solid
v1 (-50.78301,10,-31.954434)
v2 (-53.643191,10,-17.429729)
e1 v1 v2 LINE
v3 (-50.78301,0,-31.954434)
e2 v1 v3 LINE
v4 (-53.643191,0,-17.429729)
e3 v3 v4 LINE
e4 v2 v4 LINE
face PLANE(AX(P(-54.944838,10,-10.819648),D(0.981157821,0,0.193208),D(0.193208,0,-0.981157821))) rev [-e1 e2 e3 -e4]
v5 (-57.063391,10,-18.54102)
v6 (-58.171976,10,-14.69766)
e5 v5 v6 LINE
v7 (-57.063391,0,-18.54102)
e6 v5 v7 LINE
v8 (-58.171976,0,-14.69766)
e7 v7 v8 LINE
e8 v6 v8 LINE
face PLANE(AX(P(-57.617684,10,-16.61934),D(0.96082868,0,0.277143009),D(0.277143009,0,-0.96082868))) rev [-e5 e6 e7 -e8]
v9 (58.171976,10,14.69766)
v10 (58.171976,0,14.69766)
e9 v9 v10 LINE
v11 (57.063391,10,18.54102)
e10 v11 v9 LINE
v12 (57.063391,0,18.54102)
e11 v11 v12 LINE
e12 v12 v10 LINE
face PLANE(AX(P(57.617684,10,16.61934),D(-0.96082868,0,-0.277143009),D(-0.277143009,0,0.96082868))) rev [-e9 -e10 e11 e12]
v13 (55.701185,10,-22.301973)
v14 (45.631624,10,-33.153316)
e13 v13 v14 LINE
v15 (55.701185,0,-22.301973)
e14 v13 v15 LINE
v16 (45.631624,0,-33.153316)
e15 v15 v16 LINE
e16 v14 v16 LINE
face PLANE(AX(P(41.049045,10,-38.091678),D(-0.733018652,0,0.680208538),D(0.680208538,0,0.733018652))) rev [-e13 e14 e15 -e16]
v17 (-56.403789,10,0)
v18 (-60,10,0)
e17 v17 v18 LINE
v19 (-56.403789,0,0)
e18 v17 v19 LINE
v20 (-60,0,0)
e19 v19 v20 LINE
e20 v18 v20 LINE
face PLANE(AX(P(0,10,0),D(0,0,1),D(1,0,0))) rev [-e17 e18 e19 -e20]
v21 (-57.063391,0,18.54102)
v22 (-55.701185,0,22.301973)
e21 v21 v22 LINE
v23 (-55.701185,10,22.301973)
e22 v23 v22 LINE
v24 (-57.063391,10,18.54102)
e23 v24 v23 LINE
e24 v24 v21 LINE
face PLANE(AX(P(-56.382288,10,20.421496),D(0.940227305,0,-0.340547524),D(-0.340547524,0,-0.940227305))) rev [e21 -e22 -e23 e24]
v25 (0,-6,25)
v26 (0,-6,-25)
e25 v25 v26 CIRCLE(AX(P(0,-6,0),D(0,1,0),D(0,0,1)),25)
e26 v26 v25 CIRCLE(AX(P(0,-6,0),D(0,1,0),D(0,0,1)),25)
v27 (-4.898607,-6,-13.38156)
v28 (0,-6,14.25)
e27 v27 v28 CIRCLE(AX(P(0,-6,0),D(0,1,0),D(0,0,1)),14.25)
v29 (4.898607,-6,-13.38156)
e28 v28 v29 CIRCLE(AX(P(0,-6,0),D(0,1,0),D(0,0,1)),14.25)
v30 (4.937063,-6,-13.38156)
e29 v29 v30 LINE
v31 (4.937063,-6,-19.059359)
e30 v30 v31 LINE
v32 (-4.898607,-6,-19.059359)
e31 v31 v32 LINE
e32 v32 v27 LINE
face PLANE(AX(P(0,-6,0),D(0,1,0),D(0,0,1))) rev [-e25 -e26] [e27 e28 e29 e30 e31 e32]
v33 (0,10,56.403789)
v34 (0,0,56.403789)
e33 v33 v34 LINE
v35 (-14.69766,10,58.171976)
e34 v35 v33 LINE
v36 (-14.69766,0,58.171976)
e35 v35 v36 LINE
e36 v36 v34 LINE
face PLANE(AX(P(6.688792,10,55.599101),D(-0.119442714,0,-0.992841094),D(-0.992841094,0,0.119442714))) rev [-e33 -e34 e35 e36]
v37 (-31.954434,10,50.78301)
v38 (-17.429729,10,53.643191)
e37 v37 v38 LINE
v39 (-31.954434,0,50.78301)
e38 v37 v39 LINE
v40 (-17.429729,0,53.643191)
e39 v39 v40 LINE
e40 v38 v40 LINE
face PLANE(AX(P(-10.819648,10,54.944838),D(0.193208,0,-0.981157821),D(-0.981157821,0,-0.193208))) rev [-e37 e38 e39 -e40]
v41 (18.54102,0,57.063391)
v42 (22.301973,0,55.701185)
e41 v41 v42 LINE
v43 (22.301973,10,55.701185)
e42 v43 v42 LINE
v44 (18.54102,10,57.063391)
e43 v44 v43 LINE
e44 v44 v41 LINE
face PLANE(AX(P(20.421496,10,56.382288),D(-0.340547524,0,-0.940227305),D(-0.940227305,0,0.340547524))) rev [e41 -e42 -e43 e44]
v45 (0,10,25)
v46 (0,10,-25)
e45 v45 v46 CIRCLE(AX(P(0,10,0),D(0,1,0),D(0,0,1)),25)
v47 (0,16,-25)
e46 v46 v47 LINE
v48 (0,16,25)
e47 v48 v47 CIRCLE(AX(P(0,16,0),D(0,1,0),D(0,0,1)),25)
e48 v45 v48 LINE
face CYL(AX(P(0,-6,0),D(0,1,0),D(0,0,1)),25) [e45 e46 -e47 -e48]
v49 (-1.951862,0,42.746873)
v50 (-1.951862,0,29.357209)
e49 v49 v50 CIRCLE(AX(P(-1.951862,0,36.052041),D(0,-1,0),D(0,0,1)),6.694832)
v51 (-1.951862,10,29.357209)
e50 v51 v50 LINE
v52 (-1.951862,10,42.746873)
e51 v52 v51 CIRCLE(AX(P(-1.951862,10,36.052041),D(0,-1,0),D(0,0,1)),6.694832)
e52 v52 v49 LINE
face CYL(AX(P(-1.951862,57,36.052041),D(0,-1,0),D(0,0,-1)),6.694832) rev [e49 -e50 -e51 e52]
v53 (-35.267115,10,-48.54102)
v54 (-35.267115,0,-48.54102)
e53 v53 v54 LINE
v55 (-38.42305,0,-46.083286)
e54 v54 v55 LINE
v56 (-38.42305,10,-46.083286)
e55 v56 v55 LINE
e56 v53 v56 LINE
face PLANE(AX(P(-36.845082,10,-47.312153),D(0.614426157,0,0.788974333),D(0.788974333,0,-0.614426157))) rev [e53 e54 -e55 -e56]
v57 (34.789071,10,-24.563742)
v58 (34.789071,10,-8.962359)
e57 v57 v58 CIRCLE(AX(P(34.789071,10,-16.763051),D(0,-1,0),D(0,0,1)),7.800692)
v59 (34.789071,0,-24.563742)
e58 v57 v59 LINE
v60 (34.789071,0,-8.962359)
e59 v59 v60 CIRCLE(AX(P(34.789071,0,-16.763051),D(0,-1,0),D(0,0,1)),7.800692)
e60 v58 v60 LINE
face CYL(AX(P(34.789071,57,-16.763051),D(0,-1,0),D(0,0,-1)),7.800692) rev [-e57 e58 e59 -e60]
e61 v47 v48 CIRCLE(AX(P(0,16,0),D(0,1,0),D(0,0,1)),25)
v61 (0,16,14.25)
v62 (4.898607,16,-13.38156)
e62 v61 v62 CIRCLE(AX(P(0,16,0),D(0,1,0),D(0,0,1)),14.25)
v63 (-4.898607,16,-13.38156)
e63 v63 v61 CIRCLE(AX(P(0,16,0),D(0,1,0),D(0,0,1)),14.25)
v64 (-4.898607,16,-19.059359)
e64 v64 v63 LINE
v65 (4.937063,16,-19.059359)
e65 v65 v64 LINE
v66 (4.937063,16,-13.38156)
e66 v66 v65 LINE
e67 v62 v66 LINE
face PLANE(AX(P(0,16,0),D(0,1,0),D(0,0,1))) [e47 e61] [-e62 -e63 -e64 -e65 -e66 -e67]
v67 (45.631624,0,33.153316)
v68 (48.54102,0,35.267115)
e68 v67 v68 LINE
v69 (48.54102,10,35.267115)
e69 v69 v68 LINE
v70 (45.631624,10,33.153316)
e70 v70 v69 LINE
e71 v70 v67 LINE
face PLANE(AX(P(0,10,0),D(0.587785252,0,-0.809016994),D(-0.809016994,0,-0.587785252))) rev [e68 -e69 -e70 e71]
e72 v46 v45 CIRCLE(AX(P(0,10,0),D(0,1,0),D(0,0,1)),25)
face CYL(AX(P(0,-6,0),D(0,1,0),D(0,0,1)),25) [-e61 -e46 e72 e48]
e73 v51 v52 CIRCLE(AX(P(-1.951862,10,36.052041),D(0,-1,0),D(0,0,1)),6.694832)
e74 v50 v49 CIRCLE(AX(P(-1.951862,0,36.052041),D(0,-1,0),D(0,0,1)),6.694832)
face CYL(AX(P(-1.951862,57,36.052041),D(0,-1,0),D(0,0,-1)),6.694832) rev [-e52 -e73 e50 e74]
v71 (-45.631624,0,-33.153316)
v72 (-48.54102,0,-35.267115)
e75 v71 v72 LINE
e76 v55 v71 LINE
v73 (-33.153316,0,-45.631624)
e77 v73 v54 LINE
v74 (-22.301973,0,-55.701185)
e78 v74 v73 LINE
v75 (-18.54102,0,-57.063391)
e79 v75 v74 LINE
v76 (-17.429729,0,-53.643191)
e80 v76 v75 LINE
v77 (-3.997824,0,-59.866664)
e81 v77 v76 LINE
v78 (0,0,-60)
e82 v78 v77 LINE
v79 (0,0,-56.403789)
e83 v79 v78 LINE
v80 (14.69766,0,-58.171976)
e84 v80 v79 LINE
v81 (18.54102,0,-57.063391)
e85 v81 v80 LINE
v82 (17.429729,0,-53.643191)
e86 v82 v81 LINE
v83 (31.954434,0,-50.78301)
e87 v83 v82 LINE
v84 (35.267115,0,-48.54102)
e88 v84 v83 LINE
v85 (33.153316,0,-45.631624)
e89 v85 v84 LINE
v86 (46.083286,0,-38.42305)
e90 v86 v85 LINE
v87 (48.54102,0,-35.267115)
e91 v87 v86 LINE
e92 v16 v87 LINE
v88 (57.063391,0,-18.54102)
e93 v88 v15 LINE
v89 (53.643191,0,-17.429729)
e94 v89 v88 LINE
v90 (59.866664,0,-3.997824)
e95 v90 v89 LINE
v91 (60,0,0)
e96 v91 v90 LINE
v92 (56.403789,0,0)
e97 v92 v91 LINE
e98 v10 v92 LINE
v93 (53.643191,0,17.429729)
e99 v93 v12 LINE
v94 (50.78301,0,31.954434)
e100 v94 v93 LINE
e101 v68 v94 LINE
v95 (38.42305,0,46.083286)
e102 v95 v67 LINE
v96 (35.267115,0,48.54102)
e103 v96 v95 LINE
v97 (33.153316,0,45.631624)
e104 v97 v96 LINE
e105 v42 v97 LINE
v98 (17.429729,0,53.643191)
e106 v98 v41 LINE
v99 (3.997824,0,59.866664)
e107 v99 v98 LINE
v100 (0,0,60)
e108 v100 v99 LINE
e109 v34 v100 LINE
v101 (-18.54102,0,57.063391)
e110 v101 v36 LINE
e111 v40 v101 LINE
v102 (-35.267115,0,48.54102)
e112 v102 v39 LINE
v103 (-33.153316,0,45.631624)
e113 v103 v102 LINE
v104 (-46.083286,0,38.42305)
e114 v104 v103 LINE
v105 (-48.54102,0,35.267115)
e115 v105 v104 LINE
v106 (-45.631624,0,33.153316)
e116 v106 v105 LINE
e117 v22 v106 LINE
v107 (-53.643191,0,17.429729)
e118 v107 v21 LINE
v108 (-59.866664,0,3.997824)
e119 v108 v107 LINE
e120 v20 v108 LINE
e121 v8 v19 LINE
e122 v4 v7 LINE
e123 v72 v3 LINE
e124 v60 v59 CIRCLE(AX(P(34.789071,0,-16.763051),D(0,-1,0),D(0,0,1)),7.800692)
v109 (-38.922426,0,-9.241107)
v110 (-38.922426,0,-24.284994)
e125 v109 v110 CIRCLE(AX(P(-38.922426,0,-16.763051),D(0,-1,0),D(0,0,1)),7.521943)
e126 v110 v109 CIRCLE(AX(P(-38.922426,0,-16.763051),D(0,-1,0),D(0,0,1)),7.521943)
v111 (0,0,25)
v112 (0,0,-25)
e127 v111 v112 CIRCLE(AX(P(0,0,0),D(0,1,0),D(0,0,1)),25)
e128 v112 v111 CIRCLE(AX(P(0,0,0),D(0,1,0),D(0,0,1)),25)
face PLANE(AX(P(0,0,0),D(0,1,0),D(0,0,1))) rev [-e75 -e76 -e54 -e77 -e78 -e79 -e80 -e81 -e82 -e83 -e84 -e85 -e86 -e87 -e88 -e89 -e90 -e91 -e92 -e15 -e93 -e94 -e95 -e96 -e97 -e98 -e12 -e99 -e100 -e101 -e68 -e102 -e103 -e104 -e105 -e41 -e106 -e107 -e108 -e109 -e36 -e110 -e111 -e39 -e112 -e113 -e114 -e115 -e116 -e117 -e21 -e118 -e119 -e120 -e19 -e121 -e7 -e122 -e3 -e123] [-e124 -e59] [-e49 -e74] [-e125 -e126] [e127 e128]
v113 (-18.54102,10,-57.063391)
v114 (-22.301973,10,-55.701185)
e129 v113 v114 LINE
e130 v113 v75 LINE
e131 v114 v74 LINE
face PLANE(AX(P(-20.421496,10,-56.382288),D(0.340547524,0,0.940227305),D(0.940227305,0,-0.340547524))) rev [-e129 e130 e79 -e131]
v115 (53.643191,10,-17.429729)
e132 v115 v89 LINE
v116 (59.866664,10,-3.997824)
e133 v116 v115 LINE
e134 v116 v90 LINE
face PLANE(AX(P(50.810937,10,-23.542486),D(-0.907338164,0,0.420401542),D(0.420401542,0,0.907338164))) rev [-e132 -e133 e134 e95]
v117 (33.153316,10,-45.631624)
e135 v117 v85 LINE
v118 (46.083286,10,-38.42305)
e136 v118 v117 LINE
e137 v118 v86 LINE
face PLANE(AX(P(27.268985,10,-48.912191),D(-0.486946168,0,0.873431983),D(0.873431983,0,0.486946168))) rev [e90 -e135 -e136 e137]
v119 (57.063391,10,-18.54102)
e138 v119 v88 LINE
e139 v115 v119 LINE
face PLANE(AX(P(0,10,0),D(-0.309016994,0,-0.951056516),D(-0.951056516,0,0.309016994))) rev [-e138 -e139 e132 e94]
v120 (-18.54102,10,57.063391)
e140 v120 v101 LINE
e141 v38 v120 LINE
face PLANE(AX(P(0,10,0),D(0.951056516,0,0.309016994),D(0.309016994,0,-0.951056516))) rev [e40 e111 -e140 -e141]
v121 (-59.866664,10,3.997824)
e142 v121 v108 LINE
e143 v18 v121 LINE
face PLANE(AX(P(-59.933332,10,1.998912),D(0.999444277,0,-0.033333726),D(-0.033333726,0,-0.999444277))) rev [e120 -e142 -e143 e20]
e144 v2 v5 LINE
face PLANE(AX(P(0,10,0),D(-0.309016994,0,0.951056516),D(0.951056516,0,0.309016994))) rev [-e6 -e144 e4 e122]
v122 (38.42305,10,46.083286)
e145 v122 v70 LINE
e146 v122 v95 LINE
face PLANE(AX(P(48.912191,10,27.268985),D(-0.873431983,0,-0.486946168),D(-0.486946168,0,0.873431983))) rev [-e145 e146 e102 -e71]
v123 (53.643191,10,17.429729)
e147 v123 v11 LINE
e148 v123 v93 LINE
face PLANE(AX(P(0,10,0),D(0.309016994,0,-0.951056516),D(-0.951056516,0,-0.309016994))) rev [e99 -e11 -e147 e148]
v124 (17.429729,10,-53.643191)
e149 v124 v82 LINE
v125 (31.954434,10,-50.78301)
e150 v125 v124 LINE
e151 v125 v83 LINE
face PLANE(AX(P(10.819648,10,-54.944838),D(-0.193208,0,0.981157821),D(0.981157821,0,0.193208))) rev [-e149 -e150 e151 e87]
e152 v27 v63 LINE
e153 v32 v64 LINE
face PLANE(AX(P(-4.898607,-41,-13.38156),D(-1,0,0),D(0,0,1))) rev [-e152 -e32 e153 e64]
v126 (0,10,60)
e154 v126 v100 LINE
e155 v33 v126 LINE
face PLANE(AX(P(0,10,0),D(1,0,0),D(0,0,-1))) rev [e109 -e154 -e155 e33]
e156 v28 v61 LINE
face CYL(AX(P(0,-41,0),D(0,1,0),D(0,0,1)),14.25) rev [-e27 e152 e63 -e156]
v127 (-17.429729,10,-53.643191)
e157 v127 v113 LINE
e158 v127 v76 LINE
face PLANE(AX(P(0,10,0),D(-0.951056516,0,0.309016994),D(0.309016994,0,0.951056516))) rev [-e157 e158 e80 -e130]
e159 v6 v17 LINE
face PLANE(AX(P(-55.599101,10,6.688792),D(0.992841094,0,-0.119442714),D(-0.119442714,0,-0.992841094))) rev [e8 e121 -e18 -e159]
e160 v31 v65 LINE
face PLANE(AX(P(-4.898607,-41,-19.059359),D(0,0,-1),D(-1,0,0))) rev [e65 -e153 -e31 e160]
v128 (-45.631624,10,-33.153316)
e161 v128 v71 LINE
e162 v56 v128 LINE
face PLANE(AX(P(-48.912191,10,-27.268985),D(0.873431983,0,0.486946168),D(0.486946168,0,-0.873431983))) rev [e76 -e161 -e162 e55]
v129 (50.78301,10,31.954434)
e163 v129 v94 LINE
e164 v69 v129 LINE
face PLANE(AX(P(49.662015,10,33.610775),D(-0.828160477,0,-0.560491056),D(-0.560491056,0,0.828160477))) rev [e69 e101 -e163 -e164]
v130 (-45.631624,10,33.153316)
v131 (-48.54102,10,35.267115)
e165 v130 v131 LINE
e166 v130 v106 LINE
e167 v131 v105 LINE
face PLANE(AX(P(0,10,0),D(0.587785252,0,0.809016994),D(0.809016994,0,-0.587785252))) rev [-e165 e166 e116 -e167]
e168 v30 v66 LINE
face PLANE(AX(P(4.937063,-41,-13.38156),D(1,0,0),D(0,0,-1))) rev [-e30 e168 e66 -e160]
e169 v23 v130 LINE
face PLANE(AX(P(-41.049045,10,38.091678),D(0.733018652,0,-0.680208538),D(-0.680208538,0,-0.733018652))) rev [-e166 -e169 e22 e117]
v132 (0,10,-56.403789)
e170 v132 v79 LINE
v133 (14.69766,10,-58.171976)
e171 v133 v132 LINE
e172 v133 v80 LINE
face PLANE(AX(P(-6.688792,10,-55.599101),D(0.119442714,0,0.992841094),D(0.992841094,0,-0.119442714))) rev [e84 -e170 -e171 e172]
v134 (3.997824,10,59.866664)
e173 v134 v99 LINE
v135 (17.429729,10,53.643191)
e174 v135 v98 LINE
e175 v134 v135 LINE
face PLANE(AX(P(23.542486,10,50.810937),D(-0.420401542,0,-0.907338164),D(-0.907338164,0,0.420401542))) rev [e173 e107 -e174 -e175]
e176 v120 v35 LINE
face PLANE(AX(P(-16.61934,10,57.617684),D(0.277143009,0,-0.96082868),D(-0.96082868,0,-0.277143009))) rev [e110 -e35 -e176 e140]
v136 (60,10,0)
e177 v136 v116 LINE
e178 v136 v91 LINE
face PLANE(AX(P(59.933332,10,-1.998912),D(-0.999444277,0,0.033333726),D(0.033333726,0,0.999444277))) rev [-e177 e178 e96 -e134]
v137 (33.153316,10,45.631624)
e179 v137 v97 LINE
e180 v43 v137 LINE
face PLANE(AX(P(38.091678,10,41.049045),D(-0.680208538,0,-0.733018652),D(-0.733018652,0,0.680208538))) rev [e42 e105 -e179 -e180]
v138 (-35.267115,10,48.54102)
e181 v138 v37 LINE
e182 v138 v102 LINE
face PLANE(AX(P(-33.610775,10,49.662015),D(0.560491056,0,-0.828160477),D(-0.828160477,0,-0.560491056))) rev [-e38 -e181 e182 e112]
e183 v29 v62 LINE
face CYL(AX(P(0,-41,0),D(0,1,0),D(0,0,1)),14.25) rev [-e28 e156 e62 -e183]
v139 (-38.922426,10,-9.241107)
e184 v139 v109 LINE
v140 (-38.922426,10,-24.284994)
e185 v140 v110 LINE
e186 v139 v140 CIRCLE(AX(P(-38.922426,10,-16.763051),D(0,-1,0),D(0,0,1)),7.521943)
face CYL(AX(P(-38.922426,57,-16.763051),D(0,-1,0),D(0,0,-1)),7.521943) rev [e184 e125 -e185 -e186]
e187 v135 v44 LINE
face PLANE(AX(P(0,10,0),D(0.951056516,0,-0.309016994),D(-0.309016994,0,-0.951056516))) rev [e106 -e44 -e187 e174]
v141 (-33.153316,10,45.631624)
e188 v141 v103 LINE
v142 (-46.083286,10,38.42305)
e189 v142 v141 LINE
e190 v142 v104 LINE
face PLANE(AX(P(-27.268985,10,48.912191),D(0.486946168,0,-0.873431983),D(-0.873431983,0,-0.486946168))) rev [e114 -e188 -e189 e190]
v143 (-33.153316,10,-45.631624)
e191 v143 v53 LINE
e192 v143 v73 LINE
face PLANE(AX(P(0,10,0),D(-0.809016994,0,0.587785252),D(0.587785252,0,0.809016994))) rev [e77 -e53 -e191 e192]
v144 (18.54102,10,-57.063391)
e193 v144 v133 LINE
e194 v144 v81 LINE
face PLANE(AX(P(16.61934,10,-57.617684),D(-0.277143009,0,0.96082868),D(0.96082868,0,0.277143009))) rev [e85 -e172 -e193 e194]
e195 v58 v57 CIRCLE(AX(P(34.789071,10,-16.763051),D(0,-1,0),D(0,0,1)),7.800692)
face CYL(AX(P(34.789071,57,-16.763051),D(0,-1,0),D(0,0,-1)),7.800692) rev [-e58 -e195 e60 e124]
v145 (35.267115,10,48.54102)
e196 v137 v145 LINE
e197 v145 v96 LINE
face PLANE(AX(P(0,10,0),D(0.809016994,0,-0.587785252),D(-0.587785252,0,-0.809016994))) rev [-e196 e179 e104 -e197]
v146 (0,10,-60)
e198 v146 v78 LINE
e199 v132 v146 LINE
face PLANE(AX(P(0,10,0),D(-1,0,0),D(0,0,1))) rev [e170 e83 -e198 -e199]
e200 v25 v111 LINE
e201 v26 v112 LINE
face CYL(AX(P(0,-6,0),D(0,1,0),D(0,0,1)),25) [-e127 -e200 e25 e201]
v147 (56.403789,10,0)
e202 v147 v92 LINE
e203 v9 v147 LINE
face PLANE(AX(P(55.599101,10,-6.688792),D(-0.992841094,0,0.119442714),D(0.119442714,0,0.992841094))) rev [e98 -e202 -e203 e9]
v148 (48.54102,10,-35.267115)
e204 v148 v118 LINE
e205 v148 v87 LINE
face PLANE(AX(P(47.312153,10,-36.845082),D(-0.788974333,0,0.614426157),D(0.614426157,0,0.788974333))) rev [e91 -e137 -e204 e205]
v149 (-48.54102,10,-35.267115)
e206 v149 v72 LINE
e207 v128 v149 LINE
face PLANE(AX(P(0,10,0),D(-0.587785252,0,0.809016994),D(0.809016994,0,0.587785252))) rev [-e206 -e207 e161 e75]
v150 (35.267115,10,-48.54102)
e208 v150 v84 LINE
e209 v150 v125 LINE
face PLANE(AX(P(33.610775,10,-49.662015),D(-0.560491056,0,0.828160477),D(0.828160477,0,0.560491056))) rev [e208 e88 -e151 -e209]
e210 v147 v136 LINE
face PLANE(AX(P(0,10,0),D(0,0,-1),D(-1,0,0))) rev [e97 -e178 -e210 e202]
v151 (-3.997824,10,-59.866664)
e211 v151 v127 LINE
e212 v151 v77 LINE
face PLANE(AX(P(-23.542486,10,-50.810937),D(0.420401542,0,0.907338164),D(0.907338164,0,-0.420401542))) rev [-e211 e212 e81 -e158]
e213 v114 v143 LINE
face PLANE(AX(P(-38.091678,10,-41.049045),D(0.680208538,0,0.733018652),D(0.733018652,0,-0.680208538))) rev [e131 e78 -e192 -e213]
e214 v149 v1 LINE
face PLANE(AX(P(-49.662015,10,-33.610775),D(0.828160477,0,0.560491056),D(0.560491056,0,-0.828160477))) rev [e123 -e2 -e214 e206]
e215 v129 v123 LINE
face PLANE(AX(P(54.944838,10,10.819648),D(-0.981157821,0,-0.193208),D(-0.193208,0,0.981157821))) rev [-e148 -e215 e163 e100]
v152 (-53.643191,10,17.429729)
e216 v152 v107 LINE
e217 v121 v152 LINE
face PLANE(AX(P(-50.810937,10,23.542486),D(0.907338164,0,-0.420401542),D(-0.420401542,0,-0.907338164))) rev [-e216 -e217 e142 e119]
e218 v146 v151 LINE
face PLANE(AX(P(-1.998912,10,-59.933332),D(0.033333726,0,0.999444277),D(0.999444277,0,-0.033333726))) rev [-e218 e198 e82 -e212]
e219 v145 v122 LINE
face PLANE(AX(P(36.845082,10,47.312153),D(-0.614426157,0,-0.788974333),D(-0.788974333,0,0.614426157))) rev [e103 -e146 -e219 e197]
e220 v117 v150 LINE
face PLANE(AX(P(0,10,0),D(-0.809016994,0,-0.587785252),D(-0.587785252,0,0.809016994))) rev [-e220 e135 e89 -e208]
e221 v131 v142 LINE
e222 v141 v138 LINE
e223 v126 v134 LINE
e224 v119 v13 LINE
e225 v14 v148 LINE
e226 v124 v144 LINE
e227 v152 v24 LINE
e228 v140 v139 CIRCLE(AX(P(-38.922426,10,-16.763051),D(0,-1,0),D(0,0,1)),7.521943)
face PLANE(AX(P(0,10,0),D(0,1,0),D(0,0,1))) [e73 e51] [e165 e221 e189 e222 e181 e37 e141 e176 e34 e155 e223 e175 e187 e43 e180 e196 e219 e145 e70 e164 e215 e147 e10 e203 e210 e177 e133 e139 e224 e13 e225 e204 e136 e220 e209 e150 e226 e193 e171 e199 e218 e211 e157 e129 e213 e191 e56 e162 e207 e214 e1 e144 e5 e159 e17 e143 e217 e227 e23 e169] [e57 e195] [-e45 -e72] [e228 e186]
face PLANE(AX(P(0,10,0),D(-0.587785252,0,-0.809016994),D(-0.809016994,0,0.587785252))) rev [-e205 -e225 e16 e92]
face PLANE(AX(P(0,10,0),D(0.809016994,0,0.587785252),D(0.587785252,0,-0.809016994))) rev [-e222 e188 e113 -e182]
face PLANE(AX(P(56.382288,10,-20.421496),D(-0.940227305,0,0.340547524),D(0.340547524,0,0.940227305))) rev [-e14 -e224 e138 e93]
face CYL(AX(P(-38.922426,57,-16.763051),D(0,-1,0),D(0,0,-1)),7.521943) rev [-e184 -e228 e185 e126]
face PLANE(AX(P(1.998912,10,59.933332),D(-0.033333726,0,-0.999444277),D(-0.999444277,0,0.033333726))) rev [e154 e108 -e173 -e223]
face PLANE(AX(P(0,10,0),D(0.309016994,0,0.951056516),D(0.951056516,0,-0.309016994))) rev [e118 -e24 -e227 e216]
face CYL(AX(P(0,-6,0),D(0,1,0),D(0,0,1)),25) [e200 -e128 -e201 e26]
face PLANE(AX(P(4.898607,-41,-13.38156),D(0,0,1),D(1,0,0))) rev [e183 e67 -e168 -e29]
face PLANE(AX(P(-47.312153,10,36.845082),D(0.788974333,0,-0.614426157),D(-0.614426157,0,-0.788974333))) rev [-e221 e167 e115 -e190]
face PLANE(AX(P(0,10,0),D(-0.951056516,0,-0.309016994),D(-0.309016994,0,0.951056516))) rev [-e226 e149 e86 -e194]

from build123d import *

# Parameters (mm, degrees)
RATCHET_WHEEL_BODY_20T_DEPTH = 10
HUB_BOSS_50_DEPTH            = 6
HUB_BOSS_50_DEPTH_BACK       = 16
HUB_SKETCH_R                 = 25
KEYED_SHAFT_BORE_DEPTH       = 57
THROUGH_HOLES_3X_DEPTH       = 57
THROUGH_HOLES_3X_DEPTH_BACK  = 57
THROUGH_HOLES_SKETCH_R       = 7.52194346
THROUGH_HOLES_SKETCH_R_2     = 7.800691594
THROUGH_HOLES_SKETCH_R_3     = 6.694831741


with BuildPart() as part:
    # Ratchet Tooth Profile Sketch → Ratchet Wheel Body 20T (new body)
    with BuildSketch(Plane(origin=(0, 0, 0), x_dir=(1, 0, 0), z_dir=(0, 1, 0))):
        Polygon((-14.697659706, -58.171976064), (0, -56.403789421), (0, -60), (3.997824162, -59.866663528), (17.429729478, -53.643191472), (18.541019662, -57.063390978), (22.301973147, -55.701184851), (23.837157922, -54.276602012), (33.153315595, -45.631624189), (35.267115138, -48.541019662), (38.423049613, -46.083286107), (45.631624189, -33.153315595), (48.541019662, -35.267115138), (50.783010274, -31.954434238), (53.643191472, -17.429729478), (57.063390978, -18.541019662), (58.171976064, -14.697659706), (56.403789421, 0), (60, 0), (59.866663528, 3.997824162), (53.643191472, 17.429729478), (57.063390978, 18.541019662), (55.701184851, 22.301973147), (45.631624189, 33.153315595), (48.541019662, 35.267115138), (46.083286107, 38.423049613), (33.153315595, 45.631624189), (35.267115138, 48.541019662), (31.954434238, 50.783010274), (17.429729478, 53.643191472), (18.541019662, 57.063390978), (14.697659706, 58.171976064), (0, 56.403789421), (0, 60), (-3.997824162, 59.866663528), (-17.429729478, 53.643191472), (-18.541019662, 57.063390978), (-22.301973147, 55.701184851), (-33.153315595, 45.631624189), (-35.267115138, 48.541019662), (-38.423049613, 46.083286107), (-45.631624189, 33.153315595), (-48.541019662, 35.267115138), (-50.783010274, 31.954434238), (-53.643191472, 17.429729478), (-57.063390978, 18.541019662), (-58.171976064, 14.697659706), (-56.403789421, 0), (-60, 0), (-59.866663528, -3.997824162), (-53.643191472, -17.429729478), (-57.063390978, -18.541019662), (-55.701184851, -22.301973147), (-45.631624189, -33.153315595), (-48.541019662, -35.267115138), (-46.083286107, -38.423049613), (-33.153315595, -45.631624189), (-35.267115138, -48.541019662), (-31.954434238, -50.783010274), (-17.429729478, -53.643191472), (-18.541019662, -57.063390978), align=None)
    extrude(amount=RATCHET_WHEEL_BODY_20T_DEPTH)

    # Hub Sketch → Hub Boss Ø50 (add, two sides: drawn at the far end of the back side and taken through both)
    with BuildSketch(Plane(origin=(0, 10, 0), x_dir=(1, 0, 0), z_dir=(0, 1, 0)).offset(-HUB_BOSS_50_DEPTH_BACK)):
        with Locations(Location((0, 0, 0), (0, 0, 270))):
            Circle(HUB_SKETCH_R)
    extrude(amount=HUB_BOSS_50_DEPTH + HUB_BOSS_50_DEPTH_BACK)

    # Keyed Bore Sketch → Keyed Shaft Bore (cut)
    with BuildSketch(Plane(origin=(0, 16, 0), x_dir=(1, 0, 0), z_dir=(0, 1, 0))):
        with BuildLine():
            Line((4.898606828, 13.381560116), (4.937062937, 13.381560116))
            Line((4.937062937, 13.381560116), (4.937062937, 19.059359245))
            Line((4.937062937, 19.059359245), (-4.898606828, 19.059359245))
            Line((-4.898606828, 19.059359245), (-4.898606828, 13.381560116))
            ThreePointArc((-4.898606828, 13.381560116), (0, -14.25), (4.898606828, 13.381560116))
        make_face()
    extrude(amount=-KEYED_SHAFT_BORE_DEPTH, mode=Mode.SUBTRACT)

    # Through Holes Sketch → Through Holes 3x (cut, two sides: drawn at the far end of the back side and taken through both)
    with BuildSketch(Plane(origin=(0, 0, 0), x_dir=(1, 0, 0), z_dir=(0, 1, 0)).offset(-THROUGH_HOLES_3X_DEPTH_BACK)):
        with Locations(Location((-38.922426411, 16.763050903, 0), (0, 0, 270))):
            Circle(THROUGH_HOLES_SKETCH_R)
        with Locations(Location((34.789071394, 16.763050903, 0), (0, 0, 270))):
            Circle(THROUGH_HOLES_SKETCH_R_2)
        with Locations(Location((-1.951862091, -36.052040982, 0), (0, 0, 270))):
            Circle(THROUGH_HOLES_SKETCH_R_3)
    extrude(amount=THROUGH_HOLES_3X_DEPTH + THROUGH_HOLES_3X_DEPTH_BACK, mode=Mode.SUBTRACT)


solid = part.part
